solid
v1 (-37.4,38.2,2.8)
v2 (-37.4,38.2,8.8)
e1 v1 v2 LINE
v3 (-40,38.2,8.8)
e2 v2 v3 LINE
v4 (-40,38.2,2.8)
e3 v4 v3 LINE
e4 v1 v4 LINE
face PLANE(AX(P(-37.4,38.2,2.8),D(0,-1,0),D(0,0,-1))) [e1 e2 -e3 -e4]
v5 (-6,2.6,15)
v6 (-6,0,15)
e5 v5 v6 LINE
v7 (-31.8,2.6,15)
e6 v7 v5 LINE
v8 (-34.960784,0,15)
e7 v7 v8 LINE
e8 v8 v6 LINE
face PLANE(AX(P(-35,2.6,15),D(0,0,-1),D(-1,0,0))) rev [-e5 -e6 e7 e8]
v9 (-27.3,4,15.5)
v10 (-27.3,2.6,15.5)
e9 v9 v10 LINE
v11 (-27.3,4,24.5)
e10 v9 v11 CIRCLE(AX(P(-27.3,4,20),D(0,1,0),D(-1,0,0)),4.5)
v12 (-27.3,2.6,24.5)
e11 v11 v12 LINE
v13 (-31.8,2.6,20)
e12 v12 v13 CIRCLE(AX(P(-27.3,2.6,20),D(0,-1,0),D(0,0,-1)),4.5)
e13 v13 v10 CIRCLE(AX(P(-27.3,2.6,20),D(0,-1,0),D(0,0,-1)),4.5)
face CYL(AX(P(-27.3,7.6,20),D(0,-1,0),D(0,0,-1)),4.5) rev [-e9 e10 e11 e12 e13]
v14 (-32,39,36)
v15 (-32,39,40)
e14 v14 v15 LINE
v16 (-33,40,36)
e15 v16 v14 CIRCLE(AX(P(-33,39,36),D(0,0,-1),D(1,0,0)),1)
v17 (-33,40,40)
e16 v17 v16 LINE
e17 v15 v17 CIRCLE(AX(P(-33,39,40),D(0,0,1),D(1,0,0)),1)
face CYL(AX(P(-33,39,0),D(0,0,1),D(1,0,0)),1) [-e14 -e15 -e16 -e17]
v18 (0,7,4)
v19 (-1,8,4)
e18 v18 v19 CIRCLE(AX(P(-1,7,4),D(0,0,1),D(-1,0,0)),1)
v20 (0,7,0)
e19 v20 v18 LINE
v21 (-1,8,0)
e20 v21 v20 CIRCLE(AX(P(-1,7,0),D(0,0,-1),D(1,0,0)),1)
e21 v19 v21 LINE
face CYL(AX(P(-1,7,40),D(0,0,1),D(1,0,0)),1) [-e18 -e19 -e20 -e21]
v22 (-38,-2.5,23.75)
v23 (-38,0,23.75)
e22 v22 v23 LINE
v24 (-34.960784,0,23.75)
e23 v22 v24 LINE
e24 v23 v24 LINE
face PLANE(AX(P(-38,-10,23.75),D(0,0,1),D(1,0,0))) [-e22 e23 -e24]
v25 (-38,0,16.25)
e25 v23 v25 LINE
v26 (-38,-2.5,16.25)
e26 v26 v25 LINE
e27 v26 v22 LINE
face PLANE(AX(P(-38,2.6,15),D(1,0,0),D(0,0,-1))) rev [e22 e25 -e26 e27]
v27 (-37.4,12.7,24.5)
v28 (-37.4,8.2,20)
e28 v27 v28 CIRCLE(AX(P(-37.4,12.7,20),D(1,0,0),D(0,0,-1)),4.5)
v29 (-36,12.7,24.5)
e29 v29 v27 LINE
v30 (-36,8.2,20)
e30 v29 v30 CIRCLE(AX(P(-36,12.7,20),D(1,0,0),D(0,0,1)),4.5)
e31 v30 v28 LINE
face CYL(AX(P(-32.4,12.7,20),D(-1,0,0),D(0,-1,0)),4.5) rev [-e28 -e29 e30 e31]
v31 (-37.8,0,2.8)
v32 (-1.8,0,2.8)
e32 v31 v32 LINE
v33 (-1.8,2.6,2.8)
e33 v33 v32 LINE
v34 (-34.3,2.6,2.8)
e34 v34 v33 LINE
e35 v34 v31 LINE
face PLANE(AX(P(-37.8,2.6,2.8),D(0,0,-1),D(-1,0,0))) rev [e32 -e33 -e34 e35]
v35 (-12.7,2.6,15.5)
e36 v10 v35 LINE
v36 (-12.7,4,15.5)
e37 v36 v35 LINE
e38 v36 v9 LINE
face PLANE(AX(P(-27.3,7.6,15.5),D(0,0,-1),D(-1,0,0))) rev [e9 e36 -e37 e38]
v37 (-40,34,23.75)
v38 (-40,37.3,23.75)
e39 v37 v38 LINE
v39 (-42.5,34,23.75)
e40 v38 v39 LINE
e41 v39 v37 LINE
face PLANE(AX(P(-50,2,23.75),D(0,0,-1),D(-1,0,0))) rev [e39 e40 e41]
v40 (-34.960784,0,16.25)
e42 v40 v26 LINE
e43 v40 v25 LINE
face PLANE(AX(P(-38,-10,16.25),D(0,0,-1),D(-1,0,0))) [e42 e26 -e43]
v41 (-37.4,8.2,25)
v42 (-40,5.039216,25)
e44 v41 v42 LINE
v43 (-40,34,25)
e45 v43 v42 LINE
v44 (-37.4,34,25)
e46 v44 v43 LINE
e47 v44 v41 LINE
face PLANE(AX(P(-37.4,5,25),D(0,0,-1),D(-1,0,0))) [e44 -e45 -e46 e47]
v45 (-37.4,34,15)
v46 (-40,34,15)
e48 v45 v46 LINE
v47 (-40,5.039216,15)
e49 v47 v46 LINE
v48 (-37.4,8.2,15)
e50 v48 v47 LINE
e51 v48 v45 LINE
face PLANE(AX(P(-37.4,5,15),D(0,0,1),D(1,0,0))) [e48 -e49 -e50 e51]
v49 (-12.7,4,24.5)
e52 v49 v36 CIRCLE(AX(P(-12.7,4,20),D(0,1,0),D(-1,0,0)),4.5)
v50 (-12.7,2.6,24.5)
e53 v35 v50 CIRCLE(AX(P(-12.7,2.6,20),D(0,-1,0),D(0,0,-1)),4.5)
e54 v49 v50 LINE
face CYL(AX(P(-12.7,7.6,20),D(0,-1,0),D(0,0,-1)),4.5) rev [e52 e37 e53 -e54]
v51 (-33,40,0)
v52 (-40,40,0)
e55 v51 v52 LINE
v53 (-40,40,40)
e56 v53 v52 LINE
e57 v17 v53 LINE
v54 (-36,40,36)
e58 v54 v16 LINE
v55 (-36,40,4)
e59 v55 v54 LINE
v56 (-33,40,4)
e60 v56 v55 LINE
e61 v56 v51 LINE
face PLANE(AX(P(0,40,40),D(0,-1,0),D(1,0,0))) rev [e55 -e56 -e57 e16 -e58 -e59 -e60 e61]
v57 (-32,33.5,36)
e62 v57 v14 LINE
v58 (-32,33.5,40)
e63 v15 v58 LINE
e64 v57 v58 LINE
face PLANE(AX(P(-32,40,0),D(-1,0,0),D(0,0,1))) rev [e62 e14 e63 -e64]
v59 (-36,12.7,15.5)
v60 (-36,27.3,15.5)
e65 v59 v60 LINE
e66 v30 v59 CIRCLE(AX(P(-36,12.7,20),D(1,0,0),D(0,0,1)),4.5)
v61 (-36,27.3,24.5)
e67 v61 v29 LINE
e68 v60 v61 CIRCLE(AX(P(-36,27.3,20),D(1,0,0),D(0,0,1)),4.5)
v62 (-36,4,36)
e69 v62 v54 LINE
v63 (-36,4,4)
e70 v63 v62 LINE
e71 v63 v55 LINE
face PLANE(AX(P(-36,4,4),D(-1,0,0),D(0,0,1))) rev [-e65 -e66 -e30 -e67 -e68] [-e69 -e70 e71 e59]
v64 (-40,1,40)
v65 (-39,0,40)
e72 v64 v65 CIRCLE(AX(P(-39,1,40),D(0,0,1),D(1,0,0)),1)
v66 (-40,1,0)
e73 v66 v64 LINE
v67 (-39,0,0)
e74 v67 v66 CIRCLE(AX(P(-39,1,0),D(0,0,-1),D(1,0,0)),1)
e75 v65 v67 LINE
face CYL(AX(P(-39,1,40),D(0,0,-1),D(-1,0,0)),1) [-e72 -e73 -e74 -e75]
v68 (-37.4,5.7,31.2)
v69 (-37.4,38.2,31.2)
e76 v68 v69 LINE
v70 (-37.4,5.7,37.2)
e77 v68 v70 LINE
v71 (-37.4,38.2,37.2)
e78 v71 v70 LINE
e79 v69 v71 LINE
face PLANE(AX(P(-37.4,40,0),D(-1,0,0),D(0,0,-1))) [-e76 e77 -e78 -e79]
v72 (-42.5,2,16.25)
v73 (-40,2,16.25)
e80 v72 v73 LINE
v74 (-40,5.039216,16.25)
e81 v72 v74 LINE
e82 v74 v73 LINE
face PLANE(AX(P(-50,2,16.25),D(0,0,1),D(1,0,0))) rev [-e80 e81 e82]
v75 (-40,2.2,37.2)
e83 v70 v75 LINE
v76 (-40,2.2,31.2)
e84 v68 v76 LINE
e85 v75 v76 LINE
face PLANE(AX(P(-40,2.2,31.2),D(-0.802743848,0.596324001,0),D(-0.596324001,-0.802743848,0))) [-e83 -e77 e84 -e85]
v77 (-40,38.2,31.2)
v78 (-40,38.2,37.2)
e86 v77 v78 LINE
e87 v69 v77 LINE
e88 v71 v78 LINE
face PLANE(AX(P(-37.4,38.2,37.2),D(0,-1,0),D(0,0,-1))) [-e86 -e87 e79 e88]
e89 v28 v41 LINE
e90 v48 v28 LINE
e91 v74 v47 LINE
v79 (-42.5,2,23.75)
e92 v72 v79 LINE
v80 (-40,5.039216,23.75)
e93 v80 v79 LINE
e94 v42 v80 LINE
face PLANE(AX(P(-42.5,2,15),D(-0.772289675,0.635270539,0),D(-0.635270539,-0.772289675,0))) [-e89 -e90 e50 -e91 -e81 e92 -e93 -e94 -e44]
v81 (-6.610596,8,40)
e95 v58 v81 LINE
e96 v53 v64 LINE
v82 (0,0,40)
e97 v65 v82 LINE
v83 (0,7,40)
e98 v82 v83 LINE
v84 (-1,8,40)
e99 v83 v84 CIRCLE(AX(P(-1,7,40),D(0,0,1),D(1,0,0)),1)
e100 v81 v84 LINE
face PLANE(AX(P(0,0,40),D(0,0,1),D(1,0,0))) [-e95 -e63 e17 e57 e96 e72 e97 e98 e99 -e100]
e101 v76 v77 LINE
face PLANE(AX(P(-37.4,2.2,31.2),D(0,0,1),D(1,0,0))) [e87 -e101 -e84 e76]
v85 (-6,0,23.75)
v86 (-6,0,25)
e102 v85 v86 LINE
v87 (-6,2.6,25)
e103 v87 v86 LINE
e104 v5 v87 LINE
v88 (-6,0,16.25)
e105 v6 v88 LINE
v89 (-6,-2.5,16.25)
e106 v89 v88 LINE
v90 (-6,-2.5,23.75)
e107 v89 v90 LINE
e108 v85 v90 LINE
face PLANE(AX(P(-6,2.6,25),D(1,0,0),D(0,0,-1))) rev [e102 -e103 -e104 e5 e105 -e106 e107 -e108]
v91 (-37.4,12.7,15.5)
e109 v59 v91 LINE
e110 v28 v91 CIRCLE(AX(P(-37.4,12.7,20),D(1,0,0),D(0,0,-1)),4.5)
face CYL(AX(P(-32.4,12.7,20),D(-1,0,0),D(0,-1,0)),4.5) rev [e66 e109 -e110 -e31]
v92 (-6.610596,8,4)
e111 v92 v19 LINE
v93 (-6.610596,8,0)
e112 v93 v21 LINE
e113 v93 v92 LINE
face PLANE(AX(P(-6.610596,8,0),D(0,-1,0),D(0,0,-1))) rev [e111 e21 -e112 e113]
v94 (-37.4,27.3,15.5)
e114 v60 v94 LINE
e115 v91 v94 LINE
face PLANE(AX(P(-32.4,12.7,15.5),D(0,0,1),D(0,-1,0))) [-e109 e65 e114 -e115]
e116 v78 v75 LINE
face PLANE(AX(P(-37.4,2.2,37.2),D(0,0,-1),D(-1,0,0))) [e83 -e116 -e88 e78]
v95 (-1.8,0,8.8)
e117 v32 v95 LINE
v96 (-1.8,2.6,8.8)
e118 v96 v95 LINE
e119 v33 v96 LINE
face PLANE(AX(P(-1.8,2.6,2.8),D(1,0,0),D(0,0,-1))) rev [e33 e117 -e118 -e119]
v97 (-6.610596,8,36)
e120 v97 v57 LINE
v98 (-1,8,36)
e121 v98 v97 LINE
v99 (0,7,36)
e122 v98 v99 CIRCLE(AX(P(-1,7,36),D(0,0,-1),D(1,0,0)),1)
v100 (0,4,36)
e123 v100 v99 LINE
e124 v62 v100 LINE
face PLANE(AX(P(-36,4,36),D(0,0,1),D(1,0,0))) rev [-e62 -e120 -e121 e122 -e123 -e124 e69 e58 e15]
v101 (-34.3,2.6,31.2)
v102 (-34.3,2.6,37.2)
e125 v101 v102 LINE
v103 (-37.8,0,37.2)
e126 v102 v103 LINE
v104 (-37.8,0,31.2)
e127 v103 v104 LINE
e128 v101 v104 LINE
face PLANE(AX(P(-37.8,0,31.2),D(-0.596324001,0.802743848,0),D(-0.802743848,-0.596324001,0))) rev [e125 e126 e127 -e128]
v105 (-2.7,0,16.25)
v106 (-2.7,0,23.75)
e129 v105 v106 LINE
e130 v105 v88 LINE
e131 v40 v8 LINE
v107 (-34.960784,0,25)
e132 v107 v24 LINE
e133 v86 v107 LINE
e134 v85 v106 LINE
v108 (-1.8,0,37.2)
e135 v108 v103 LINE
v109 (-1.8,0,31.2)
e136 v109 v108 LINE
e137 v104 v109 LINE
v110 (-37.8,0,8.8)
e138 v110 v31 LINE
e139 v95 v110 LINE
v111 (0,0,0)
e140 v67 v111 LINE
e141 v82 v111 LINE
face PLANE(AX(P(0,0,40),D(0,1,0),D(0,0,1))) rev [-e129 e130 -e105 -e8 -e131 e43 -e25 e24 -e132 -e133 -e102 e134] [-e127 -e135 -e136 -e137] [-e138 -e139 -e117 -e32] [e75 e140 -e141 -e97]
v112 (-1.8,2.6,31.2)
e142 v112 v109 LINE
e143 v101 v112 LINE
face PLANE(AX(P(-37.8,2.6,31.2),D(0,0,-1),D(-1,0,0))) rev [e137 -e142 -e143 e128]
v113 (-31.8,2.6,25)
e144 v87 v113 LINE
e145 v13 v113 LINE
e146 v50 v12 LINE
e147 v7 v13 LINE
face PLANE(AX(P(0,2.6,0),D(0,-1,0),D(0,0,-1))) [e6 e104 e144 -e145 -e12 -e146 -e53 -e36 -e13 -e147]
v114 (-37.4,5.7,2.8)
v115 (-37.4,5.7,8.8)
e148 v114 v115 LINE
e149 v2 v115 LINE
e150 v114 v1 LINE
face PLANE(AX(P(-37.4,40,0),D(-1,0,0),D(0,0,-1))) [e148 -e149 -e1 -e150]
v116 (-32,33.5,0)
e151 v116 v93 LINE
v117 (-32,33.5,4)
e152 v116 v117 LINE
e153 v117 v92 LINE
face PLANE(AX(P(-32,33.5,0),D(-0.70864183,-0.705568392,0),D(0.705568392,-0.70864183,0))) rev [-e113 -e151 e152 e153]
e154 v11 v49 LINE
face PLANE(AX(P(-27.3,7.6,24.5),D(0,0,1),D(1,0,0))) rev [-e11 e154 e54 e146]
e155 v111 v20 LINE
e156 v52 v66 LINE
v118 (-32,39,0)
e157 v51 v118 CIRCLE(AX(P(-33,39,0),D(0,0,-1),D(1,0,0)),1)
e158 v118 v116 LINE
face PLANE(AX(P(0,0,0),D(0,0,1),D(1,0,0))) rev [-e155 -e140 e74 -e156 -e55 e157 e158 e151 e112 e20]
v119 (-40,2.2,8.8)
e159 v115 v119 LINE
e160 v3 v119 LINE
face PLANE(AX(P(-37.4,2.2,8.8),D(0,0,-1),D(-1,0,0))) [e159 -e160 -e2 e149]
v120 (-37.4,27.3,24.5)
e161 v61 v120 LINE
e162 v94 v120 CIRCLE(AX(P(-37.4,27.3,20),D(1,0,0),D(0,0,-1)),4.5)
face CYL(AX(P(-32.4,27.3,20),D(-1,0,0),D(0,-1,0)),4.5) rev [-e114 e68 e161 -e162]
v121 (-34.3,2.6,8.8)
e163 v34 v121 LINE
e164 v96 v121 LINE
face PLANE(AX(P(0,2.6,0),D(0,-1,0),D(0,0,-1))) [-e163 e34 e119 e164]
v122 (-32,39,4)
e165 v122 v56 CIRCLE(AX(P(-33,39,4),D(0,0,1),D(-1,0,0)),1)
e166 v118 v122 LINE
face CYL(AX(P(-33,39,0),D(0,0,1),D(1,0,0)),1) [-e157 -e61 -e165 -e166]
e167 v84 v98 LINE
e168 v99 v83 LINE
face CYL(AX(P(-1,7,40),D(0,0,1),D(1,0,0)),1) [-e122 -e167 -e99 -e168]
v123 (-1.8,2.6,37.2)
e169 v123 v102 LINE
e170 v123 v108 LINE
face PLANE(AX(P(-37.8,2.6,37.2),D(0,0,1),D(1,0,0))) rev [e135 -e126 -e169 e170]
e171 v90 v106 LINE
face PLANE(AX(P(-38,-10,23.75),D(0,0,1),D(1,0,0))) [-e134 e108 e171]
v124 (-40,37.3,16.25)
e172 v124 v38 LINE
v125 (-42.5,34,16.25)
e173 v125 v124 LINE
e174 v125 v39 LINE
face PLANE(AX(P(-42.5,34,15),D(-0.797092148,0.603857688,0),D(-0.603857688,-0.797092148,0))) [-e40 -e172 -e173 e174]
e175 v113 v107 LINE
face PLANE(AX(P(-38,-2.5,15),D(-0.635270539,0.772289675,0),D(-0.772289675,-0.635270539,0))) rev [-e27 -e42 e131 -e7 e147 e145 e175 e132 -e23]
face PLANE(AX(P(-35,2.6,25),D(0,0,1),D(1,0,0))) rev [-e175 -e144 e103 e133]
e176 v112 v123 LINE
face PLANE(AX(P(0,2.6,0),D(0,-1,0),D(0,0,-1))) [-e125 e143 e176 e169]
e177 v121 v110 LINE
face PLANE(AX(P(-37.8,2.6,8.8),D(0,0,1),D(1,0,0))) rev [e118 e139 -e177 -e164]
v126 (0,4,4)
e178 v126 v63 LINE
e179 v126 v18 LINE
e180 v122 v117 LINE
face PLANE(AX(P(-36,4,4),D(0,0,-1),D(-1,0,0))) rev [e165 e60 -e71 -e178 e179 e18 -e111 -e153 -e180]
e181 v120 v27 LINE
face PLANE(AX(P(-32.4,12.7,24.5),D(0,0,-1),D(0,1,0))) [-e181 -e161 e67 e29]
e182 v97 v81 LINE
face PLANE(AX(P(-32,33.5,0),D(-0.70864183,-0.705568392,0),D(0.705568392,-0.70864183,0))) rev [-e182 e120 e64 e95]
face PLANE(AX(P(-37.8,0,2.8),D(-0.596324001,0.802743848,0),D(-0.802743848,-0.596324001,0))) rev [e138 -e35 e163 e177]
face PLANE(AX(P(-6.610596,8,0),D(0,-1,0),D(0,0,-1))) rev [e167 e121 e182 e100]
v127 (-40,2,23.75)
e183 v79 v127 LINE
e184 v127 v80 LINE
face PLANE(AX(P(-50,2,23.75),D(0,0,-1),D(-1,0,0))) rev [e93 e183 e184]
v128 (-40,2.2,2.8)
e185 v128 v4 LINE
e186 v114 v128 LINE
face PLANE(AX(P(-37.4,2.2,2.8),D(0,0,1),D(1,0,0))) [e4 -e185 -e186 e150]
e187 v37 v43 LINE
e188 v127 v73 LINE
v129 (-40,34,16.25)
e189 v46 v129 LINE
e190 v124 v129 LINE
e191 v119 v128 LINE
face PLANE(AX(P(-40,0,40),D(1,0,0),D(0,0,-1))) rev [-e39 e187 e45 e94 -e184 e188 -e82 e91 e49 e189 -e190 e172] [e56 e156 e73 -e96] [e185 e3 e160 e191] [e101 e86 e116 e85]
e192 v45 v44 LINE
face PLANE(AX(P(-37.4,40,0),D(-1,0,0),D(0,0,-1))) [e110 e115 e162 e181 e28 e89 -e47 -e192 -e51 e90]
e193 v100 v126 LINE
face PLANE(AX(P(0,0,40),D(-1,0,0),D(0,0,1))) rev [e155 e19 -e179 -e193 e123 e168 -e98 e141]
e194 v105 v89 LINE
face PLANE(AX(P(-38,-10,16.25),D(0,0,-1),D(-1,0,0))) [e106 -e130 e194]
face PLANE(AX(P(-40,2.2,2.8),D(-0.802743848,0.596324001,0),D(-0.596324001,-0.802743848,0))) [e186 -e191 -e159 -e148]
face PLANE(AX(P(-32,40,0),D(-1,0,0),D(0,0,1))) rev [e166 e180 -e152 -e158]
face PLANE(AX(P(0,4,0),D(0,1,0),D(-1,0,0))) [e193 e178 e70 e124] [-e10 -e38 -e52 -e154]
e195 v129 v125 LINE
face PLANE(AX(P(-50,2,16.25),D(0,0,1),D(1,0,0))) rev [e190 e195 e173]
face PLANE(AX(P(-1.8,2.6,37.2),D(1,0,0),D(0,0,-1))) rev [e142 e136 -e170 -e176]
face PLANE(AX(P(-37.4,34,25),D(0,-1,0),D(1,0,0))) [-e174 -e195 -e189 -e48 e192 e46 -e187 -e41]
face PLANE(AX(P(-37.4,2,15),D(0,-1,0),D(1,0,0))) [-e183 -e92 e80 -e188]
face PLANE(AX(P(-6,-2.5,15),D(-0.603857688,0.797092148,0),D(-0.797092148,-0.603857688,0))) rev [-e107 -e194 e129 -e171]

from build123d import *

# Parameters (mm, degrees)
SKETCH1_W            = 40
SKETCH1_H            = 40
BOSS_EXTRUDE1_DEPTH  = 40
CUT_EXTRUDE1_DEPTH   = 40
SKETCH3_W            = 36
SKETCH3_H            = 32
CUT_EXTRUDE2_DEPTH   = 36
SKETCH4_W            = 36
SKETCH4_H            = 6
SKETCH4_W_2          = 29
SKETCH4_H_2          = 10
CUT_EXTRUDE3_DEPTH   = 2.6
BOSS_EXTRUDE2_DEPTH  = 10
SKETCH6_W            = 35.3
SKETCH6_H            = 1.25
CUT_EXTRUDE4_DEPTH   = 10
BOSS_EXTRUDE3_DEPTH  = 6
LPATTERN1_COUNT      = 2
LPATTERN1_PITCH      = 28.4
CUT_EXTRUDE5_DEPTH   = 5
MIRROR1_COPY_1_DEPTH = 6
FILLET1_R            = 1


with BuildPart() as part:
    # Sketch1 → Boss-Extrude1 (new body)
    with BuildSketch(Plane.XY):
        with Locations((-20, 20)):
            Rectangle(SKETCH1_W, SKETCH1_H)
    extrude(amount=BOSS_EXTRUDE1_DEPTH)

    # Sketch2 → Cut-Extrude1 (cut)
    with BuildSketch(Plane.XY.offset(40)):
        Polygon((-32, 40), (-32, 33.5), (-6.610595609, 8), (0, 8), (17.085067255, 36.265731876), (-7.495565519, 45.713912599), align=None)
    extrude(amount=-CUT_EXTRUDE1_DEPTH, mode=Mode.SUBTRACT)

    # Sketch3 → Cut-Extrude2 (cut)
    with BuildSketch(Plane(origin=(0, 40, 0), x_dir=(1, 0, 0), z_dir=(0, 1, 0))):
        with Locations((-18, -20)):
            Rectangle(SKETCH3_W, SKETCH3_H)
    extrude(amount=-CUT_EXTRUDE2_DEPTH, mode=Mode.SUBTRACT)

    # Sketch4 → Cut-Extrude3 (cut)
    with BuildSketch(Plane.XZ):
        with Locations((-19.8, 34.2)):
            Rectangle(SKETCH4_W, SKETCH4_H)
        with Locations((-20.5, 20)):
            Rectangle(SKETCH4_W_2, SKETCH4_H_2)
        with Locations((-19.8, 5.8)):
            Rectangle(SKETCH4_W, SKETCH4_H)
    cut_extrude3 = extrude(amount=-CUT_EXTRUDE3_DEPTH, mode=Mode.SUBTRACT)

    # Sketch5 → Boss-Extrude2 (add)
    with BuildSketch(Plane(origin=(0, 0, 25), x_dir=(-1, 0, 0), z_dir=(0, 0, -1))):
        Polygon((31.8, 2.6), (35, 2.6), (38, 2.6), (38, -2.5), align=None)
        Polygon((6, 0), (6, -2.5), (2.7, 0), align=None)
    boss_extrude2 = extrude(amount=BOSS_EXTRUDE2_DEPTH)

    # Sketch6 → Cut-Extrude4 (cut)
    with BuildSketch(Plane.XZ):
        with Locations((-20.35, 15.625)):
            Rectangle(SKETCH6_W, SKETCH6_H)
        with Locations((-20.35, 24.375)):
            Rectangle(SKETCH6_W, SKETCH6_H)
    cut_extrude4 = extrude(amount=CUT_EXTRUDE4_DEPTH, mode=Mode.SUBTRACT)

    # Sketch7 → Boss-Extrude3 (add)
    with BuildSketch(Plane(origin=(0, 0, 8.8), x_dir=(-1, 0, 0), z_dir=(0, 0, -1))):
        Polygon((37.8, 0), (34.3, 2.6), (37.8, 2.6), align=None)
    boss_extrude3 = extrude(amount=BOSS_EXTRUDE3_DEPTH)

    # LPattern1: Boss-Extrude3 ×2
    with Locations(*[(0, 0, i * LPATTERN1_PITCH) for i in range(1, LPATTERN1_COUNT)]):
        add(boss_extrude3)

    # Sketch9 → Cut-Extrude5 (cut)
    with BuildSketch(Plane.XZ.offset(-2.6)):
        with BuildLine():
            Line((-27.3, 24.5), (-12.7, 24.5))
            ThreePointArc((-12.7, 24.5), (-8.2, 20), (-12.7, 15.5))
            Line((-12.7, 15.5), (-27.3, 15.5))
            ThreePointArc((-27.3, 15.5), (-31.8, 20), (-27.3, 24.5))
        make_face()
    cut_extrude5 = extrude(amount=-CUT_EXTRUDE5_DEPTH, mode=Mode.SUBTRACT)

    # Mirror1: Cut-Extrude3, Boss-Extrude2, Cut-Extrude4, Boss-Extrude3, Cut-Extrude5 across plane
    add(cut_extrude3.mirror(Plane(origin=(-20, 20, 0), x_dir=(0, 0, 1), z_dir=(-0.7071067811865475, 0.7071067811865477, 0))), mode=Mode.SUBTRACT)
    add(boss_extrude2.mirror(Plane(origin=(-20, 20, 0), x_dir=(0, 0, 1), z_dir=(-0.7071067811865475, 0.7071067811865477, 0))))
    add(cut_extrude4.mirror(Plane(origin=(-20, 20, 0), x_dir=(0, 0, 1), z_dir=(-0.7071067811865475, 0.7071067811865477, 0))), mode=Mode.SUBTRACT)
    add(boss_extrude3.mirror(Plane(origin=(-20, 20, 0), x_dir=(0, 0, 1), z_dir=(-0.7071067811865475, 0.7071067811865477, 0))))
    add(cut_extrude5.mirror(Plane(origin=(-20, 20, 0), x_dir=(0, 0, 1), z_dir=(-0.7071067811865475, 0.7071067811865477, 0))), mode=Mode.SUBTRACT)

    # Mirror1 copy 1 sketch → Mirror1 copy 1 (add)
    with BuildSketch(Plane(origin=(-40, 40, 37.2), x_dir=(0, -1, 0), z_dir=(0, 0, -1))):
        Polygon((37.8, 0), (34.3, -2.6), (37.8, -2.6), align=None)
    extrude(amount=MIRROR1_COPY_1_DEPTH)

    # Fillet1
    fillet1_edges = [part.edges().sort_by_distance(p)[0] for p in [
        (-32, 40, 2),
        (0, 8, 2),
        (-32, 40, 38),
        (0, 8, 38),
        (-40, 0, 20),
    ]]
    fillet(fillet1_edges, radius=FILLET1_R)


solid = part.part
